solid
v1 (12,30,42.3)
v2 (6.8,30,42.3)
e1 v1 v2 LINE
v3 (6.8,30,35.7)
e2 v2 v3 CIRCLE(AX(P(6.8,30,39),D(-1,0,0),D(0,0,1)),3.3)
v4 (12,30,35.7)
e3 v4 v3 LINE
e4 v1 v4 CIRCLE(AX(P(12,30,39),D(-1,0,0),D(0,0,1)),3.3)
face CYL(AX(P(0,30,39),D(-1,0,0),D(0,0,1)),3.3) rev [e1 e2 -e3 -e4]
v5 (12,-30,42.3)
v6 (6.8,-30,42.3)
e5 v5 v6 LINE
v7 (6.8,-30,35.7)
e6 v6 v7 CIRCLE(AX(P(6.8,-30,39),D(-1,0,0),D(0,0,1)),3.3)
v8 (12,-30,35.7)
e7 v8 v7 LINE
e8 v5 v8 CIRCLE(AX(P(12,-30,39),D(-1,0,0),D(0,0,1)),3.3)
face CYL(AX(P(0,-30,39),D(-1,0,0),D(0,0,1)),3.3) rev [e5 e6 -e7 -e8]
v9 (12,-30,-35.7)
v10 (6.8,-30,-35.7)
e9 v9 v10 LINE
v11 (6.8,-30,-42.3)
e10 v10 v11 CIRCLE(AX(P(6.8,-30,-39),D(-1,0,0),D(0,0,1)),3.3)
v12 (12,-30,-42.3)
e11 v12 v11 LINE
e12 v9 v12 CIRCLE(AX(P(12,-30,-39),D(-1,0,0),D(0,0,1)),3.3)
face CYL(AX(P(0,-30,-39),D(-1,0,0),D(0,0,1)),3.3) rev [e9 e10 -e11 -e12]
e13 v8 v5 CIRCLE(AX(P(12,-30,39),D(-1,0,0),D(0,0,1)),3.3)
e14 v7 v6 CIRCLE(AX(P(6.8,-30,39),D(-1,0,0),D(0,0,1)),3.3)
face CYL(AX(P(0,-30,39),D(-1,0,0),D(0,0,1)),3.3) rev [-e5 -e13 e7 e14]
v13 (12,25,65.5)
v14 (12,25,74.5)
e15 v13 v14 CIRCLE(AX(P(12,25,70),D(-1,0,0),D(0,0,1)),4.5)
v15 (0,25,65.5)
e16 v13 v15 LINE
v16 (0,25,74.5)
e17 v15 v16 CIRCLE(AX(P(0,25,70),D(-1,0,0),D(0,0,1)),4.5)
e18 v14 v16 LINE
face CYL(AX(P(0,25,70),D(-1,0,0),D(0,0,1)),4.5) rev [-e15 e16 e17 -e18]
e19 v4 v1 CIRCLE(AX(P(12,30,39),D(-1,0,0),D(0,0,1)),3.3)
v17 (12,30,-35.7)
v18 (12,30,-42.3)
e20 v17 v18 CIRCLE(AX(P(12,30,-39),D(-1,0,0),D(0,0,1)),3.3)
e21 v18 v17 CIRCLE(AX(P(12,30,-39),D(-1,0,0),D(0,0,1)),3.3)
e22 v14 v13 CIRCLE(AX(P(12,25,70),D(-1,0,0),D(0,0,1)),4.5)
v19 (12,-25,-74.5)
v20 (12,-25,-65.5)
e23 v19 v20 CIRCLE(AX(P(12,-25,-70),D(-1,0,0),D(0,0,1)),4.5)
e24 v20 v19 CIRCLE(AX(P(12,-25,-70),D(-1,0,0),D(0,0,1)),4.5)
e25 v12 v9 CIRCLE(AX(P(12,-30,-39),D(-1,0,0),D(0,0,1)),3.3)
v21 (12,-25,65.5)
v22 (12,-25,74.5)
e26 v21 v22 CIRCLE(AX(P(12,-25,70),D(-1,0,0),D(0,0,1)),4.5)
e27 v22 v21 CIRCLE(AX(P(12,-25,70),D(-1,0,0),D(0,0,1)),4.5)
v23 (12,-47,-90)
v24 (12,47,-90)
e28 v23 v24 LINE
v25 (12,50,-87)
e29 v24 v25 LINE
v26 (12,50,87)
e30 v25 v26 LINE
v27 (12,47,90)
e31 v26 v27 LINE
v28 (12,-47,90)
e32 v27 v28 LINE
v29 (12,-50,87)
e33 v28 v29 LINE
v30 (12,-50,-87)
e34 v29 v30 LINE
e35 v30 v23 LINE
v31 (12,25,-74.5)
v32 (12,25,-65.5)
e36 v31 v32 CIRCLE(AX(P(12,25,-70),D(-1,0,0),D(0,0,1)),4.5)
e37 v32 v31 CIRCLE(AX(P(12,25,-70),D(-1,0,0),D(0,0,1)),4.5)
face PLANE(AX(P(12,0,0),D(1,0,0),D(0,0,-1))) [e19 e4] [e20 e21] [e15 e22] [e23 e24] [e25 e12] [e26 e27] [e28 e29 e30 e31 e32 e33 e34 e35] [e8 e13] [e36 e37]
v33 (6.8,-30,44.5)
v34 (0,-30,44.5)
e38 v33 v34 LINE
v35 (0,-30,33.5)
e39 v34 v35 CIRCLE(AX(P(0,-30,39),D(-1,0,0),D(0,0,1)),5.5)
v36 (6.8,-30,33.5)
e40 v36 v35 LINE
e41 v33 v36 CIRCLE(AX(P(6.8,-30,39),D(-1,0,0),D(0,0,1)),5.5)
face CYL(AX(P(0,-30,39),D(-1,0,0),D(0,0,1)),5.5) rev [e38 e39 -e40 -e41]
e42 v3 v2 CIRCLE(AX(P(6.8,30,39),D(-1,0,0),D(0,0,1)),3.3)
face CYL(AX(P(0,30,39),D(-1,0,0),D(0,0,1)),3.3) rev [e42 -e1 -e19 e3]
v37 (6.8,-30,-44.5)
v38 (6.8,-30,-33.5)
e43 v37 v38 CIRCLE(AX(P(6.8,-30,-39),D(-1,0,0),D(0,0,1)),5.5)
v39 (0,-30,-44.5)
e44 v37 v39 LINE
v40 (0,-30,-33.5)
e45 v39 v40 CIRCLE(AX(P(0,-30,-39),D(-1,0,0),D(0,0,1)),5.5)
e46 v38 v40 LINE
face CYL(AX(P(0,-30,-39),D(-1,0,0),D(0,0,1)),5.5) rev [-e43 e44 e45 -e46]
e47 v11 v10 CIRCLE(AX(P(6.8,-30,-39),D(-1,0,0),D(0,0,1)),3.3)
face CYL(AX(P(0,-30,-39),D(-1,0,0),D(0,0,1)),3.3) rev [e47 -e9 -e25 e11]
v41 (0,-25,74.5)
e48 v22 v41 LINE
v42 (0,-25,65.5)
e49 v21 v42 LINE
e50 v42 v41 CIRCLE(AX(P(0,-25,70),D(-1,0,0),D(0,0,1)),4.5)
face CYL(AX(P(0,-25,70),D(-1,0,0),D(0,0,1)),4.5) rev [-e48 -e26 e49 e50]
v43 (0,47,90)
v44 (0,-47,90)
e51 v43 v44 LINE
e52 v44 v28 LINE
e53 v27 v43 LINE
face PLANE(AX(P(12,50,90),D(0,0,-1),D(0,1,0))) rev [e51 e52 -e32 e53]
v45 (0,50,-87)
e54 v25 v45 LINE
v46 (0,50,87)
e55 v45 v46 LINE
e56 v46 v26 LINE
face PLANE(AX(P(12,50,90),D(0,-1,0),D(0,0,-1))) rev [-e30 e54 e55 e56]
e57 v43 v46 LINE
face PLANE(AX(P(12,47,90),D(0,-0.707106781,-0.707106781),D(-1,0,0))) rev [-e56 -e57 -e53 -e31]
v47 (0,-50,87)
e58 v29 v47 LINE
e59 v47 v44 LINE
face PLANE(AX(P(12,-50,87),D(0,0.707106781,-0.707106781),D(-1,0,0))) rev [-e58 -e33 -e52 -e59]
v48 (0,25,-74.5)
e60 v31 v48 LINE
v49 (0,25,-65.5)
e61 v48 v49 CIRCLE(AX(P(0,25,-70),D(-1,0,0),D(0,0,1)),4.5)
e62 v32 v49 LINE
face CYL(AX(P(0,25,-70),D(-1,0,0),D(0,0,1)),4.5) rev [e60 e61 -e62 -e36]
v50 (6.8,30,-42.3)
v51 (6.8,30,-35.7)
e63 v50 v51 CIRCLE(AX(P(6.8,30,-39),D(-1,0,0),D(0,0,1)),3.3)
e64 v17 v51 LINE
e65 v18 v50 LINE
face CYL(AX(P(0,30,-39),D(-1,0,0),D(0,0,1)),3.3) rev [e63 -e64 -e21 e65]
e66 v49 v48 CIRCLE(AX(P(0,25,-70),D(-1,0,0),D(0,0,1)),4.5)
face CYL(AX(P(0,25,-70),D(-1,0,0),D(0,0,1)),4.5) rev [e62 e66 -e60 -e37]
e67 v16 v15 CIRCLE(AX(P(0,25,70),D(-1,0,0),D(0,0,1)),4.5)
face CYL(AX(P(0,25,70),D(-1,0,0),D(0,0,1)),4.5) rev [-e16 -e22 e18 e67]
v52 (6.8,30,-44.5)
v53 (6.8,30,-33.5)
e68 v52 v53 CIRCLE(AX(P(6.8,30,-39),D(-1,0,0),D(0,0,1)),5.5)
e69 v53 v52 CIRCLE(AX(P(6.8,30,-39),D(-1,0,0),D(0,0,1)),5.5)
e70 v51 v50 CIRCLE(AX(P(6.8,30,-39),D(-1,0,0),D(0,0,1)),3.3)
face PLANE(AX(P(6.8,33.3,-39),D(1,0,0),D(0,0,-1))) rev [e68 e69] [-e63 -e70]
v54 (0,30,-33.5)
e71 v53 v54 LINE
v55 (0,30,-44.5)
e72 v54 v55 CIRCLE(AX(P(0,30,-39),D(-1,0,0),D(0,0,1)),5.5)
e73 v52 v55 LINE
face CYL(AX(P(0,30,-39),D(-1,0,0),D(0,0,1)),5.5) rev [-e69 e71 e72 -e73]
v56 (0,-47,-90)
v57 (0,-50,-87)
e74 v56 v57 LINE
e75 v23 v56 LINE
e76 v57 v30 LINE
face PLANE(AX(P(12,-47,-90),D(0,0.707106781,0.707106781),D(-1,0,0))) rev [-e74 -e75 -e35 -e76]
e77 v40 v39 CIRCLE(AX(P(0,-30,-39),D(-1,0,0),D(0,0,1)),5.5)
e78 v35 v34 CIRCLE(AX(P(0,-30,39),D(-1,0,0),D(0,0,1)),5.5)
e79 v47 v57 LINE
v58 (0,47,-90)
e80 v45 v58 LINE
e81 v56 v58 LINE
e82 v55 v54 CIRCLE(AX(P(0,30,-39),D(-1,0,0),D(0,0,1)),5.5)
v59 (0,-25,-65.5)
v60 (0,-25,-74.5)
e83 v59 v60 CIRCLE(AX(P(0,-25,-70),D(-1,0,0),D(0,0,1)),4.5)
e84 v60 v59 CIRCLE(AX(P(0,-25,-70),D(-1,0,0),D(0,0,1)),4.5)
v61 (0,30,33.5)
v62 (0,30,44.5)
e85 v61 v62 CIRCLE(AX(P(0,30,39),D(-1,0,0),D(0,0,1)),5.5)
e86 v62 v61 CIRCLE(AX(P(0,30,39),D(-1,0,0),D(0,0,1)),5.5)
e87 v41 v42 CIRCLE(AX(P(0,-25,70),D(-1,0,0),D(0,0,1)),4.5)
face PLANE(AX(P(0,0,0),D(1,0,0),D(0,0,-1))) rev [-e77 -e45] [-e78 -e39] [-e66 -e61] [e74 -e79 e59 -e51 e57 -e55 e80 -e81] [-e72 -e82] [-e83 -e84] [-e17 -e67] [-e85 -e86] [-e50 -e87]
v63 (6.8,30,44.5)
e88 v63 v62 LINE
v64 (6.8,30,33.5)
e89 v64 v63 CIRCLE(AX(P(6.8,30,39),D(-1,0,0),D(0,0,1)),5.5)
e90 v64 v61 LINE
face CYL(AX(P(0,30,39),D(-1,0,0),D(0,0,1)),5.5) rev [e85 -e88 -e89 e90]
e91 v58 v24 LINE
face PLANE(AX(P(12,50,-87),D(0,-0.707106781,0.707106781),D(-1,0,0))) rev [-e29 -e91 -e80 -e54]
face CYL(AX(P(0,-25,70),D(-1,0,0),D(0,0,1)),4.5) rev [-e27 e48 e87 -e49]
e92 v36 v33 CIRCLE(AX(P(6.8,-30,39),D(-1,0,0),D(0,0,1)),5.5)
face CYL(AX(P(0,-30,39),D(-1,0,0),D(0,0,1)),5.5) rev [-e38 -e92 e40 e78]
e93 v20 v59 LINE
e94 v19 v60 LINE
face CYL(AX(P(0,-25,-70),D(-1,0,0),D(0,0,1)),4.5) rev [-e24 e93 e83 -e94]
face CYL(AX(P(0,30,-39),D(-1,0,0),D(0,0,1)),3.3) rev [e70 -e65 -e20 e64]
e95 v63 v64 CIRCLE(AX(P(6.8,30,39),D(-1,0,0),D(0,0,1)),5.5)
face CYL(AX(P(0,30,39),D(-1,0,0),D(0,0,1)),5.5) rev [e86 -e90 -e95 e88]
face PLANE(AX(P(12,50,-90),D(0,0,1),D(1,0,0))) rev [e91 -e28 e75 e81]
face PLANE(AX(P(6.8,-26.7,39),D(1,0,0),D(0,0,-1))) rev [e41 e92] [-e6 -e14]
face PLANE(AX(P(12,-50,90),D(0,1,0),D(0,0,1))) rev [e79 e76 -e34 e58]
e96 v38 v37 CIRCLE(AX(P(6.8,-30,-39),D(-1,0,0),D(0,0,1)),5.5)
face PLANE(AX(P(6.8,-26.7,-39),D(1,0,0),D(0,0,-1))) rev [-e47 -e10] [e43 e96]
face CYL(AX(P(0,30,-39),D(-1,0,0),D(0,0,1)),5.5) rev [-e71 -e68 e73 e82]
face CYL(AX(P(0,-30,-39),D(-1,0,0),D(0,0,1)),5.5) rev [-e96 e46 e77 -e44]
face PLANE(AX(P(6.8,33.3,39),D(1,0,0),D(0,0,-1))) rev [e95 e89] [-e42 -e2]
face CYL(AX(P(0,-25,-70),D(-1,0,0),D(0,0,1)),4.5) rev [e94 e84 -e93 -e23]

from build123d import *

# Parameters (mm, degrees)
SKETCH_1_W                = 180
SKETCH_1_H                = 100
EXTRUDE_1_DEPTH           = 12
HOLE_WIZARD_1_D           = 6.6
HOLE_WIZARD_1_CBORE_D     = 11
HOLE_WIZARD_1_CBORE_DEPTH = 6.8
HOLE_WIZARD_9_0_9_1_D     = 9
CHAMFER_1_SIZE            = 3


with BuildPart() as part:
    # 草图1 → 凸台-拉伸1 (new body)
    with BuildSketch(Plane(origin=(0, 0, 0), x_dir=(0, 0, -1), z_dir=(1, 0, 0))):
        Rectangle(SKETCH_1_W, SKETCH_1_H)
    extrude(amount=EXTRUDE_1_DEPTH)

    # 打孔尺寸(%根据)内六角圆柱头螺钉的类型1 (through all)
    with Locations(Plane.ZY):
        with Locations((-39, 30), (-39, -30), (39, 30), (39, -30)):
            CounterBoreHole(HOLE_WIZARD_1_D / 2, HOLE_WIZARD_1_CBORE_D / 2, HOLE_WIZARD_1_CBORE_DEPTH)

    # Ø9.0 (9) 直径孔1 (through all)
    with Locations(Plane.ZY):
        with Locations((-70, 25), (-70, -25), (70, 25), (70, -25)):
            Hole(HOLE_WIZARD_9_0_9_1_D / 2)

    # 倒角1
    chamfer_1_edges = [part.edges().sort_by_distance(p)[0] for p in [
        (6, -50, -90),
        (6, -50, 90),
        (6, 50, 90),
        (6, 50, -90),
    ]]
    chamfer(chamfer_1_edges, length=CHAMFER_1_SIZE)


solid = part.part
